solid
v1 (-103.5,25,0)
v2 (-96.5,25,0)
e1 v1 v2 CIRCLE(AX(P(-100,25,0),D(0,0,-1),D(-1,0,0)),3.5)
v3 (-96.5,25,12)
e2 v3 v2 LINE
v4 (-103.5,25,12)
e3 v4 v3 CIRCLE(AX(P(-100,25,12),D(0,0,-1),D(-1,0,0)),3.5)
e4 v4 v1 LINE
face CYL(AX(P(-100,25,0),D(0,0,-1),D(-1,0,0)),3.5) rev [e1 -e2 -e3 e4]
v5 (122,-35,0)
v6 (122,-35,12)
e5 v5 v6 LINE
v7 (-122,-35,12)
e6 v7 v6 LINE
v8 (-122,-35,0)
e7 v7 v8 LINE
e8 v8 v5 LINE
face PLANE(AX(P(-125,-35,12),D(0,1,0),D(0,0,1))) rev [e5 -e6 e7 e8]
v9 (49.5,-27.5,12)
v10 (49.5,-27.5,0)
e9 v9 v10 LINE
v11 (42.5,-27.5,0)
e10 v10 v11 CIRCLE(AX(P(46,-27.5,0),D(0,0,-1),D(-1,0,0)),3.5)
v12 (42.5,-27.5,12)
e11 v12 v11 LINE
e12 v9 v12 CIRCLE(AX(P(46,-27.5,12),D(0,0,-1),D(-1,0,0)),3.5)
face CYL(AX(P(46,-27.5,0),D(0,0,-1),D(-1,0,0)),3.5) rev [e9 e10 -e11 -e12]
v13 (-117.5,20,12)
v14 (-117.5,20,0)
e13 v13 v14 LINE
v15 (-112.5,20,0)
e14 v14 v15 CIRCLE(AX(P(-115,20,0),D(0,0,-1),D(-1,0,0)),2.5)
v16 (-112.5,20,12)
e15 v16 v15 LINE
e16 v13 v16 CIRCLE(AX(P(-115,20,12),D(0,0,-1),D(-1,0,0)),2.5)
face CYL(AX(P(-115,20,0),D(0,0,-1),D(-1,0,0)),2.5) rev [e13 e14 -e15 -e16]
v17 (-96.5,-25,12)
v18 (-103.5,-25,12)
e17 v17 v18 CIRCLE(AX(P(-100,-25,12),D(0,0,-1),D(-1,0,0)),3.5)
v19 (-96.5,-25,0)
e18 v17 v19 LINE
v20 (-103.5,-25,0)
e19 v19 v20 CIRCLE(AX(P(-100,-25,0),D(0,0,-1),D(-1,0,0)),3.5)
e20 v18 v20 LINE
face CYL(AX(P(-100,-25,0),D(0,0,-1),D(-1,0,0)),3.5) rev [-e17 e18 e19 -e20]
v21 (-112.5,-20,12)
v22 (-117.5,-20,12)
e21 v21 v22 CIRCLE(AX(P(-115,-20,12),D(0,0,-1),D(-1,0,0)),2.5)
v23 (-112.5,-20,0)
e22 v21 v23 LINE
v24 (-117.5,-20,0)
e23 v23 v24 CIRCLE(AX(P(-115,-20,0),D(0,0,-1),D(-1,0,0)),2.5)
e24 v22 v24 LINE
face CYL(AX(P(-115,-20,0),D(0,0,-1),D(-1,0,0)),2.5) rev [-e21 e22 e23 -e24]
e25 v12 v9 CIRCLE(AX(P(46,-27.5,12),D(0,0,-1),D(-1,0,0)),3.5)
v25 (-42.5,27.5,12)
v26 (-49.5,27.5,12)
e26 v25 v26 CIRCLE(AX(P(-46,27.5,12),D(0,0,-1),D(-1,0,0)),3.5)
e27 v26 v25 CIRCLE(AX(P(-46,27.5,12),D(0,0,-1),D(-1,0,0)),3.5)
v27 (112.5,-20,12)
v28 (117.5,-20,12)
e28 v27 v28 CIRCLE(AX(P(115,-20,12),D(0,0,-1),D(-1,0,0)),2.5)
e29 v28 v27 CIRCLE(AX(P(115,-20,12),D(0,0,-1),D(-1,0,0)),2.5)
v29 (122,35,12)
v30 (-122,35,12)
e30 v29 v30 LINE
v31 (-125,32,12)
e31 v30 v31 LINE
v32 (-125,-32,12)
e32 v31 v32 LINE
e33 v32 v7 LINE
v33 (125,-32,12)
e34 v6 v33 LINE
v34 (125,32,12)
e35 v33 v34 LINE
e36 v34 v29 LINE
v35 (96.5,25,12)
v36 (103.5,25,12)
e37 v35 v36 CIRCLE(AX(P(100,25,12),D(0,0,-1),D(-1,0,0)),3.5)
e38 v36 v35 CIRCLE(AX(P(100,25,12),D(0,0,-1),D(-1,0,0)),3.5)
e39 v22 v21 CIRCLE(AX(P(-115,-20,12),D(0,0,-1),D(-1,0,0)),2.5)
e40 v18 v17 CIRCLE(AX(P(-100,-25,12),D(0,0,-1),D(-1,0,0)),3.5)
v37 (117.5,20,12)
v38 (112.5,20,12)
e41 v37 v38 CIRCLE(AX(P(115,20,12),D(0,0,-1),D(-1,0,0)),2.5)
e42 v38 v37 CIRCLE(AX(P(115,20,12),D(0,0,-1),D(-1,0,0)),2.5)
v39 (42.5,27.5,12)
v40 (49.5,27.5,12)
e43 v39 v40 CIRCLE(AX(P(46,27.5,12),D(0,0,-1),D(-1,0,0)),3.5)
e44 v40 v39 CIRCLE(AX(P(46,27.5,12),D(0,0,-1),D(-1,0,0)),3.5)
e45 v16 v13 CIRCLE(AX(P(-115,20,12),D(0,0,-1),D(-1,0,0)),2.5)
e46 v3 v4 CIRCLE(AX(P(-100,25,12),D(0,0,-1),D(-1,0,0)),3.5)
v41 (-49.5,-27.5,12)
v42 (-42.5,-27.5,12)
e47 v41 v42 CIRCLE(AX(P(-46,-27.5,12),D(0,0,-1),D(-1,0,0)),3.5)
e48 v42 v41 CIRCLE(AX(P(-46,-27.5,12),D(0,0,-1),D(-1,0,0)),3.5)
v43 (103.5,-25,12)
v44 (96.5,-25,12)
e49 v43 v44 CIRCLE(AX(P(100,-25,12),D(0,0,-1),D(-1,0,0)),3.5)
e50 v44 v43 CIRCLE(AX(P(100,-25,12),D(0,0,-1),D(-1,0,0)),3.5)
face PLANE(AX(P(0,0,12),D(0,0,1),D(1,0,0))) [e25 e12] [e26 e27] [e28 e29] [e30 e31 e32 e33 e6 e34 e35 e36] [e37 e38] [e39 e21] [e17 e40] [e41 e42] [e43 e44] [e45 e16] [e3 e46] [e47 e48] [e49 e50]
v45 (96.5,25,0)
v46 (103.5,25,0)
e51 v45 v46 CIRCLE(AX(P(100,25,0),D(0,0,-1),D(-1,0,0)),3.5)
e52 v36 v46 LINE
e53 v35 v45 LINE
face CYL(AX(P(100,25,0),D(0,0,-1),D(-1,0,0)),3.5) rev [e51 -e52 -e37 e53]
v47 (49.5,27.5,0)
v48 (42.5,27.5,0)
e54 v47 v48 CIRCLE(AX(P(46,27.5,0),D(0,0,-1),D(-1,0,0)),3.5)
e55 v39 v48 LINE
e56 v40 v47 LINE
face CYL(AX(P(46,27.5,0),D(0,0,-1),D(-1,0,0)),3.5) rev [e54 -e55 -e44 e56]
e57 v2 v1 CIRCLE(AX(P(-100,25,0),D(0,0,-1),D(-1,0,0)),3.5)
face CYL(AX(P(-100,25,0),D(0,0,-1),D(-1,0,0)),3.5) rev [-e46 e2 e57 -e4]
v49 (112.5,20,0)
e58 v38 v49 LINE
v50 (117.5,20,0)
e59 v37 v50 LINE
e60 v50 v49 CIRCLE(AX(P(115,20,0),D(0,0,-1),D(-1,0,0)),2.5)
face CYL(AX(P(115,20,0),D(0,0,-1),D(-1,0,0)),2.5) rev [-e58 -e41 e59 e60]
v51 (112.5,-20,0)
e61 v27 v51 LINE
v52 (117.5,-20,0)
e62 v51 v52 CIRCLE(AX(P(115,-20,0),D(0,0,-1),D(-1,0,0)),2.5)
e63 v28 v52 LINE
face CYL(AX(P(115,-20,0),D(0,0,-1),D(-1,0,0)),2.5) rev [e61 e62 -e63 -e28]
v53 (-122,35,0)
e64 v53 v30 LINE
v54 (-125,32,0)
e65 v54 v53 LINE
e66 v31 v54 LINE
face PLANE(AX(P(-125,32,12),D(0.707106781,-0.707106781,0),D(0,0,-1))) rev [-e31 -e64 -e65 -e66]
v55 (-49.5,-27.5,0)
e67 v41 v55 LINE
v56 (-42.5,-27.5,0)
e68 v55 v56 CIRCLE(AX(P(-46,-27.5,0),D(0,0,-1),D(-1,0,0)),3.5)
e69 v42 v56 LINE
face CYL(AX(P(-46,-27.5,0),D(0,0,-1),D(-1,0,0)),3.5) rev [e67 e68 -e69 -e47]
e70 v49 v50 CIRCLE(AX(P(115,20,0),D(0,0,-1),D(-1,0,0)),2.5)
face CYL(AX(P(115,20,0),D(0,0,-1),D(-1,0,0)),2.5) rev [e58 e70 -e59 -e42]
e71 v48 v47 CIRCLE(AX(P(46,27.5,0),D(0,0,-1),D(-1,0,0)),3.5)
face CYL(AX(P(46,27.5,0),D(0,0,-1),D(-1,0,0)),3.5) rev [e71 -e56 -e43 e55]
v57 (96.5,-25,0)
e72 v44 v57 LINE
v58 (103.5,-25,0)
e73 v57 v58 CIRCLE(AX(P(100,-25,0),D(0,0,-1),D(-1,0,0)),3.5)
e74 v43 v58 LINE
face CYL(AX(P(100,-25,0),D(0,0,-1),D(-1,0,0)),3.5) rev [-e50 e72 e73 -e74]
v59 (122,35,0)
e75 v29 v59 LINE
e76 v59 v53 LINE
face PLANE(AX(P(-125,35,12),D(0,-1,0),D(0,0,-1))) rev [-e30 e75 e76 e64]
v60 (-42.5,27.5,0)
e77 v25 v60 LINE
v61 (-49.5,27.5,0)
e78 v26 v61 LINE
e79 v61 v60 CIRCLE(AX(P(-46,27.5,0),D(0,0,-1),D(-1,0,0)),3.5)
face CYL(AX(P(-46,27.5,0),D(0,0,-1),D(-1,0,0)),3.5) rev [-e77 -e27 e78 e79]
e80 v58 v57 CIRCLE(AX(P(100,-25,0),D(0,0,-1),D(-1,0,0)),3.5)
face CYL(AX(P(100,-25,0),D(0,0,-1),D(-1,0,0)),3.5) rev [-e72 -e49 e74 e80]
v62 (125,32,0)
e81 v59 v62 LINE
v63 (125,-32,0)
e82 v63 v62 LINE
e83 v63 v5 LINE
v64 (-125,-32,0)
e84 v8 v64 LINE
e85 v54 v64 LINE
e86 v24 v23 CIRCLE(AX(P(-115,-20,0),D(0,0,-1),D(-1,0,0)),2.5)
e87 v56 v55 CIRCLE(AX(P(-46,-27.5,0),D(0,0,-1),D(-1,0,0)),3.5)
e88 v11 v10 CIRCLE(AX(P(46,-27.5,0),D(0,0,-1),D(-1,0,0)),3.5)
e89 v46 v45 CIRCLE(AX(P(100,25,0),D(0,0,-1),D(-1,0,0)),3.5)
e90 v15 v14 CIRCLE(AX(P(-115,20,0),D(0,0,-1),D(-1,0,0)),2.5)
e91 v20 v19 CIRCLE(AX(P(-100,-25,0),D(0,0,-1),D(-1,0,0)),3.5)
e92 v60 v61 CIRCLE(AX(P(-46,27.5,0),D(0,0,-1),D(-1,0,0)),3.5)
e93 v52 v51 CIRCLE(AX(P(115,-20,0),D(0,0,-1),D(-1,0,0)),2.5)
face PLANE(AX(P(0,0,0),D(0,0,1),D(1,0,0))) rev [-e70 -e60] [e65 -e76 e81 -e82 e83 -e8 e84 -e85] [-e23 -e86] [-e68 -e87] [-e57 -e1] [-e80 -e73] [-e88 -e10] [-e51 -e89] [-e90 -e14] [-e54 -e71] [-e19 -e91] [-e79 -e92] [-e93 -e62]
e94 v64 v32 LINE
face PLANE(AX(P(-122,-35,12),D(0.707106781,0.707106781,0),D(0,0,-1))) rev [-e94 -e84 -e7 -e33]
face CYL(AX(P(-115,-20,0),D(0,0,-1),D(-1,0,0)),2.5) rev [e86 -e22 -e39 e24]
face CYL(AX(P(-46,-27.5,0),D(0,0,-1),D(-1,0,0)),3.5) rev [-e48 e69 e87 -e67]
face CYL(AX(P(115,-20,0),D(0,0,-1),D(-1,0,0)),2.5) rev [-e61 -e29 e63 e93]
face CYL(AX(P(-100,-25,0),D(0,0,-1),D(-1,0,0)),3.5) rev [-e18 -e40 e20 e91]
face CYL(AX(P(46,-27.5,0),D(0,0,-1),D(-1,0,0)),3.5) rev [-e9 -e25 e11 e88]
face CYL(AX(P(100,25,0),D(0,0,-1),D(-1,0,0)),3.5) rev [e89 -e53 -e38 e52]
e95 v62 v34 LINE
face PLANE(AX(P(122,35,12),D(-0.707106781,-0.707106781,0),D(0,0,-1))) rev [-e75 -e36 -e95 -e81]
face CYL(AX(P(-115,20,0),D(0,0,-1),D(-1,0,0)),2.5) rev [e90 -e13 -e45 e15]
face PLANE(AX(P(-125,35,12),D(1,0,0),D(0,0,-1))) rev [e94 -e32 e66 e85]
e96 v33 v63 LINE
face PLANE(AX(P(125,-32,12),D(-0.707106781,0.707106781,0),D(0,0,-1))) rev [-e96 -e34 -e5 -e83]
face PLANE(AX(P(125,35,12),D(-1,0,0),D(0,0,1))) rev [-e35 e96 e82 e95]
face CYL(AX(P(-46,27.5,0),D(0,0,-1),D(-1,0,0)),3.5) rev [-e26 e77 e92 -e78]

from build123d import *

# Parameters (mm, degrees)
SKETCH_1_W            = 250
SKETCH_1_H            = 70
EXTRUDE_1_DEPTH       = 12
CHAMFER_1_SIZE        = 3
HOLE_WIZARD_7_0_7_1_D = 7
HOLE_WIZARD_M6_1_D    = 5
HOLE_WIZARD_7_0_7_2_D = 7


with BuildPart() as part:
    # 草图1 → 凸台-拉伸1 (new body)
    with BuildSketch(Plane.XY):
        Rectangle(SKETCH_1_W, SKETCH_1_H)
    extrude(amount=EXTRUDE_1_DEPTH)

    # 倒角1
    chamfer_1_edges = [part.edges().sort_by_distance(p)[0] for p in [
        (125, -35, 6),
        (-125, -35, 6),
        (-125, 35, 6),
        (125, 35, 6),
    ]]
    chamfer(chamfer_1_edges, length=CHAMFER_1_SIZE)

    # Ø7.0 (7) 直径孔1 (through all)
    with Locations(Plane(origin=(0, 0, 0), x_dir=(-1, 0, 0), z_dir=(0, 0, -1))):
        with Locations((100, -25), (100, 25), (-100, 25), (-100, -25)):
            Hole(HOLE_WIZARD_7_0_7_1_D / 2)

    # M6 螺纹孔1 (through all)
    with Locations(Plane(origin=(0, 0, 0), x_dir=(-1, 0, 0), z_dir=(0, 0, -1))):
        with Locations((115, -20), (115, 20), (-115, 20), (-115, -20)):
            Hole(HOLE_WIZARD_M6_1_D / 2)

    # Ø7.0 (7) 直径孔2 (through all)
    with Locations(Plane(origin=(0, 0, 0), x_dir=(-1, 0, 0), z_dir=(0, 0, -1))):
        with Locations((46, 27.5), (46, -27.5), (-46, 27.5), (-46, -27.5)):
            Hole(HOLE_WIZARD_7_0_7_2_D / 2)


solid = part.part
